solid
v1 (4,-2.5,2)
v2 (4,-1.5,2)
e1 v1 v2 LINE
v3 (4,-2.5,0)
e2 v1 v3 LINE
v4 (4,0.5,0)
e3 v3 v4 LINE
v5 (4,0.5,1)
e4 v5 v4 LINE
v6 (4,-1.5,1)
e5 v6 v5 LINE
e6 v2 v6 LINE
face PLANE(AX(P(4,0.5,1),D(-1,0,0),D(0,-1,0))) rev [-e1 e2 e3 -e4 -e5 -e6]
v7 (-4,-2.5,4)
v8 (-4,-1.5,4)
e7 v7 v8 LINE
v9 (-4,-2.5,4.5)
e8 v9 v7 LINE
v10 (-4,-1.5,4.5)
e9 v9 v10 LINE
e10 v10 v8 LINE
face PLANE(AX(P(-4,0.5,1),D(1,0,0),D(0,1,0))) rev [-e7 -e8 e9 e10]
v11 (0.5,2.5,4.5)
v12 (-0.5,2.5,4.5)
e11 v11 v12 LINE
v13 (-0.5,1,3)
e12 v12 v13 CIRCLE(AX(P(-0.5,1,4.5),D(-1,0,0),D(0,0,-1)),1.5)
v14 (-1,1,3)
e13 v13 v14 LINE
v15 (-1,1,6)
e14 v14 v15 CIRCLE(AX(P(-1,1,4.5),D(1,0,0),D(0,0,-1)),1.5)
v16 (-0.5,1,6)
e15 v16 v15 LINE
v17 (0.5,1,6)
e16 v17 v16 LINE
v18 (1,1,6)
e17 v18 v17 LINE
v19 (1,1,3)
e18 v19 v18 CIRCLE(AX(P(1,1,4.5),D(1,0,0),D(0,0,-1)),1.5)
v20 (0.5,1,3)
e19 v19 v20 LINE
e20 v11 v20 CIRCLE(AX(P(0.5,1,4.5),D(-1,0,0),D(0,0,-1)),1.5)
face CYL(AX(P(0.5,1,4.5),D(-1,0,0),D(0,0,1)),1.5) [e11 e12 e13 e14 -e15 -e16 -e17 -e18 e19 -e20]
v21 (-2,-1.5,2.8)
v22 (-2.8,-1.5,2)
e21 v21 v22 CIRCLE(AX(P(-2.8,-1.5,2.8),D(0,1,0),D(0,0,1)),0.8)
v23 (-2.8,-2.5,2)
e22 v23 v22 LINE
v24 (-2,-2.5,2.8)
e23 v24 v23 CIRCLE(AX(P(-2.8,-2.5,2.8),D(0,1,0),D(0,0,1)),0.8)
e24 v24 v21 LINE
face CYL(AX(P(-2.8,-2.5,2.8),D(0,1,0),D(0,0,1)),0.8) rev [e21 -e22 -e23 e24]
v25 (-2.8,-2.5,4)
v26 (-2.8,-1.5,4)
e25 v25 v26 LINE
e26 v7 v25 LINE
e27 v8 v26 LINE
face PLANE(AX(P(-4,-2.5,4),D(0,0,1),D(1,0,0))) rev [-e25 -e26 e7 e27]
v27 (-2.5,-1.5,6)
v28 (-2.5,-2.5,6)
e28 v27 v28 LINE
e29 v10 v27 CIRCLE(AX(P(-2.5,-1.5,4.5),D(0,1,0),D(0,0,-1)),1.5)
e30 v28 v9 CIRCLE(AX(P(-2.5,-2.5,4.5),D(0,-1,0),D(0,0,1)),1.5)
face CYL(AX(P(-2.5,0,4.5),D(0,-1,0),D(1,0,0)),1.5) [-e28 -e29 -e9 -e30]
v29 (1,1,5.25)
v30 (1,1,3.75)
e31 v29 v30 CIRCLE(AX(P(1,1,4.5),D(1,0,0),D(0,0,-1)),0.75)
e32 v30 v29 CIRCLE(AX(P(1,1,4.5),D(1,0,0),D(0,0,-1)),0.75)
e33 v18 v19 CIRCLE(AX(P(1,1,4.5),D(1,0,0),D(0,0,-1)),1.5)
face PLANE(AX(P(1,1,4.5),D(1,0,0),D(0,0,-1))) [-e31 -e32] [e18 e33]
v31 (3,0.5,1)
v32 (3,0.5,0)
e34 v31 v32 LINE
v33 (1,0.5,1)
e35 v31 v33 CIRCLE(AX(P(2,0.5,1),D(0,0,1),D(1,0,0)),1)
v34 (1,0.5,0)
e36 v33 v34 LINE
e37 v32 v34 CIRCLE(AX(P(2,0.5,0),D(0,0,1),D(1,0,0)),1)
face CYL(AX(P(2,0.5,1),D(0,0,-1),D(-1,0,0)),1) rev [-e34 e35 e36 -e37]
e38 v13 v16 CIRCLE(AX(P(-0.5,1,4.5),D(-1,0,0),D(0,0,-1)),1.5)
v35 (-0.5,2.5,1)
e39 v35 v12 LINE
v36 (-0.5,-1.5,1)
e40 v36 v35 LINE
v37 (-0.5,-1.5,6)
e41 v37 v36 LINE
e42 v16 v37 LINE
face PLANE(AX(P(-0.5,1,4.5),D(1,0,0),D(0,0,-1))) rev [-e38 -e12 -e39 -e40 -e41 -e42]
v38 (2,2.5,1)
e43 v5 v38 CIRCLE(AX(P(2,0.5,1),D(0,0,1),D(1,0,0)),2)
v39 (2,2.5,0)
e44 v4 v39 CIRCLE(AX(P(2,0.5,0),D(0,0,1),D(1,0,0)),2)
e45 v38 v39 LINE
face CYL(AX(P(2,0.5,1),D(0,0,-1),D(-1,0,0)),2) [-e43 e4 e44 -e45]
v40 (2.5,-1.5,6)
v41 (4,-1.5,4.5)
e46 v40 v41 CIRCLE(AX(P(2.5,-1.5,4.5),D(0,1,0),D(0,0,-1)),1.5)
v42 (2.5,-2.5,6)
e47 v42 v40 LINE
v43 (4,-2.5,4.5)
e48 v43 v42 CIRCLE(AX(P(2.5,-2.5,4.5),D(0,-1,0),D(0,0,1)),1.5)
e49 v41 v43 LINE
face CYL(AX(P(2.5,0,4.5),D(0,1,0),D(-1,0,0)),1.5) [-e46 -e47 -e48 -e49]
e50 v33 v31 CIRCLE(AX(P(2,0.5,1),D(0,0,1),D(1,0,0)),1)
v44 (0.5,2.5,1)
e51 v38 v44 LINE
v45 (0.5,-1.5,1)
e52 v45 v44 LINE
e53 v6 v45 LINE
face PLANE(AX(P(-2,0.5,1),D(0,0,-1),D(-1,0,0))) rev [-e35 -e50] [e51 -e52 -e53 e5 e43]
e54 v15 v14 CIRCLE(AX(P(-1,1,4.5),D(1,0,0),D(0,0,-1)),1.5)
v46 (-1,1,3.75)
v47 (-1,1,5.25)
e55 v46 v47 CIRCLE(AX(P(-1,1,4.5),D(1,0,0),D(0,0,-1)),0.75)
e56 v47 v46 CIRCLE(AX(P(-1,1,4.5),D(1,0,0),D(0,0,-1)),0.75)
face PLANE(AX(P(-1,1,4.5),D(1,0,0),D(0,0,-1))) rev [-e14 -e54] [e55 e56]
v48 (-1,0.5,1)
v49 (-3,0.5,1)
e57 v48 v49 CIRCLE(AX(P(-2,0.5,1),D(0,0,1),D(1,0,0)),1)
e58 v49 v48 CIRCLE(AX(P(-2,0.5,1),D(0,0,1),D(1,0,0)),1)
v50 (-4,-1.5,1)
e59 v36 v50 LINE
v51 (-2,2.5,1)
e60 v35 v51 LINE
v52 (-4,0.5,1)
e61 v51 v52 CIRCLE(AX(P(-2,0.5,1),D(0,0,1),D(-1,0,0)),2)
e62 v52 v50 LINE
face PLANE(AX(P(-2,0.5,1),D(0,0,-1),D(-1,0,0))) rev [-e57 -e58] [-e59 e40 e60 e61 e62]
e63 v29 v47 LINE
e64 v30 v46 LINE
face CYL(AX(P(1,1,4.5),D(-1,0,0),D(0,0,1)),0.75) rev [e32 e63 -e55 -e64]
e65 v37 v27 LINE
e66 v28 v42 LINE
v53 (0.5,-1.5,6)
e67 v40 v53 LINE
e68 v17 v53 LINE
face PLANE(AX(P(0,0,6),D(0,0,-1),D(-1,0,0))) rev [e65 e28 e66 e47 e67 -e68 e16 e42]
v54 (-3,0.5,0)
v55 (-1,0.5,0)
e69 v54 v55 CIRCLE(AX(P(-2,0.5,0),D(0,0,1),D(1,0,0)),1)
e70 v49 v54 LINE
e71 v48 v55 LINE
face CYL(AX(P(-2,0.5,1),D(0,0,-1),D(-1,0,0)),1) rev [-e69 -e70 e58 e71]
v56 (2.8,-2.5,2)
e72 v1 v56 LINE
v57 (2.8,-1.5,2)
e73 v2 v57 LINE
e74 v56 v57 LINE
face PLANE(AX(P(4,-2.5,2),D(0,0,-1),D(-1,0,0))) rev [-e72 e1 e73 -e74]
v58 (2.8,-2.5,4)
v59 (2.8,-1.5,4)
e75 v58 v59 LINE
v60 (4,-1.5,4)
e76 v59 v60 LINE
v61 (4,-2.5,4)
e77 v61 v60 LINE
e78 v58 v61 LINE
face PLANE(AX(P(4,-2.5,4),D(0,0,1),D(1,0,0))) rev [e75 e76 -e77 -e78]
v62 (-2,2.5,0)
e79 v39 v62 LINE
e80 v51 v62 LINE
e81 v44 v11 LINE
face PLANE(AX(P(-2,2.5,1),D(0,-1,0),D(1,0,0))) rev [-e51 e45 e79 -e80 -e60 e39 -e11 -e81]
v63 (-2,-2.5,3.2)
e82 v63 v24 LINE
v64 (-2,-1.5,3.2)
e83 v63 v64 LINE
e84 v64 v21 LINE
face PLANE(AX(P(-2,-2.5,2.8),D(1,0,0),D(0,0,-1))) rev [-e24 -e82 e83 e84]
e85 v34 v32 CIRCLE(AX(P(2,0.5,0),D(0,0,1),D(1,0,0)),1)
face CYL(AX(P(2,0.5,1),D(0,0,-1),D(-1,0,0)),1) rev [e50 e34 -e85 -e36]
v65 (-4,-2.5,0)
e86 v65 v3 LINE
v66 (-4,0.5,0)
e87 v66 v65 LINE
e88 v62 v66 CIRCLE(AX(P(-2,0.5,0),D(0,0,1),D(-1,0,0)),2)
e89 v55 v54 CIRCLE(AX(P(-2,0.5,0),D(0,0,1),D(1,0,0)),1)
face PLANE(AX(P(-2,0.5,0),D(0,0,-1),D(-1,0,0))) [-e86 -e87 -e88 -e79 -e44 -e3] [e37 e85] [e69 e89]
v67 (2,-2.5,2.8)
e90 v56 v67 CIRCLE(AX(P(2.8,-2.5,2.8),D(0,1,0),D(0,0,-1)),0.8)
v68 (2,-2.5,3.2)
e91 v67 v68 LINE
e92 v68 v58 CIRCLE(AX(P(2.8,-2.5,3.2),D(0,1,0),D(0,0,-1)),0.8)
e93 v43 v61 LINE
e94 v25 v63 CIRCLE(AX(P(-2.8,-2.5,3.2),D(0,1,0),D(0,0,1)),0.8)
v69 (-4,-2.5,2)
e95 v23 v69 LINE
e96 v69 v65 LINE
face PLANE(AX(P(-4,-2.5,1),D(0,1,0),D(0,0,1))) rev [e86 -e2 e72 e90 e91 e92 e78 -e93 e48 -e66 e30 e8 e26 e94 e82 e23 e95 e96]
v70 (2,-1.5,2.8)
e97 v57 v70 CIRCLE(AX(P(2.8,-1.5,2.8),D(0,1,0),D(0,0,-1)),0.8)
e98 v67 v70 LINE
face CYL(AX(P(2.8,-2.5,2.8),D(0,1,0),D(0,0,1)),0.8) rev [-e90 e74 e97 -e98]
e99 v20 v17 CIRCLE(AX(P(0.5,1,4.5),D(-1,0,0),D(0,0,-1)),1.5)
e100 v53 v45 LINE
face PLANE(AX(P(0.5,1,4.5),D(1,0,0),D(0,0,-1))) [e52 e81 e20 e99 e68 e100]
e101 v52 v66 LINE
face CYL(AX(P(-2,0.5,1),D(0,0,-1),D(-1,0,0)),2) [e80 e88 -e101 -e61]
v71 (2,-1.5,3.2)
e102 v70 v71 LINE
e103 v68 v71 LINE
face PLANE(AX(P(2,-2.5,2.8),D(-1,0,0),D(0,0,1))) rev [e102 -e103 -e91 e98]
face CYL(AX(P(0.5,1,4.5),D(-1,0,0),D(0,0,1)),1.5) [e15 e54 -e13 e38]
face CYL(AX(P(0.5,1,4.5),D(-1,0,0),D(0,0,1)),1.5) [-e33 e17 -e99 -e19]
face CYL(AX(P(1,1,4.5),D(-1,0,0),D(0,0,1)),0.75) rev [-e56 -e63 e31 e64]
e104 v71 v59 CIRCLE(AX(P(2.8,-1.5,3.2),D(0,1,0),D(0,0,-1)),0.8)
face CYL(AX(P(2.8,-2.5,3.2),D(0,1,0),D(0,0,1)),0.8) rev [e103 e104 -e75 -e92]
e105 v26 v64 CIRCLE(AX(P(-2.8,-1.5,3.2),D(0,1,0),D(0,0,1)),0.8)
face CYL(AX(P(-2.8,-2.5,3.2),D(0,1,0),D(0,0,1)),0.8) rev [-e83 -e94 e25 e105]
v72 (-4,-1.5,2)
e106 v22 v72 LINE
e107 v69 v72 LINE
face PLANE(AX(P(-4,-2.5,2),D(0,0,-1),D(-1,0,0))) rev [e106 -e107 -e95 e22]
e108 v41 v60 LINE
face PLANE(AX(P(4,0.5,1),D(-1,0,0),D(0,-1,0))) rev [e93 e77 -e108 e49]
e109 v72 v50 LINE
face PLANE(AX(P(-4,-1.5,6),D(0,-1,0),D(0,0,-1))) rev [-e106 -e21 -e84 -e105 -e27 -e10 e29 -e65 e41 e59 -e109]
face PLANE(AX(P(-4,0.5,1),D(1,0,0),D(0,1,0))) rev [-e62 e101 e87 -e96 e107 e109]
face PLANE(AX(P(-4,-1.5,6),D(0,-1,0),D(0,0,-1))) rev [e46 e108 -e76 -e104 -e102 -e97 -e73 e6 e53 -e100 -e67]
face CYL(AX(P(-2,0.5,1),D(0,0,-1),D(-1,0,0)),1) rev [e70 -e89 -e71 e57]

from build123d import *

# Parameters (mm, degrees)
BASE_PLATE_SKETCH_R        = 1
BASE_PLATE_DEPTH           = 1
UPRIGHT_WALL_SKETCH_W      = 8
UPRIGHT_WALL_SKETCH_H      = 1
UPRIGHT_WALL_DEPTH         = 5
SLOT_CUTS_DEPTH            = 9.246211251
SIDE_LUG_DEPTH             = 0.5
PIN_BOSS_SKETCH_R          = 1.5
PIN_BOSS_SKETCH_R_2        = 0.75
PIN_BOSS_3_DEPTH           = 1
PIN_BORE_SKETCH_R          = 0.75
PIN_BORE_DEPTH             = 8.90569415
UPRIGHT_WALL_FILLET_R1_5_R = 1.5


with BuildPart() as part:
    # Base Plate Sketch → Base Plate (new body)
    with BuildSketch(Plane.XY):
        with BuildLine():
            Line((-2, 2.5), (2, 2.5))
            ThreePointArc((2, 2.5), (3.414213562, 1.914213562), (4, 0.5))
            Line((4, 0.5), (4, -2.5))
            Line((4, -2.5), (-4, -2.5))
            Line((-4, -2.5), (-4, 0.5))
            ThreePointArc((-4, 0.5), (-3.414213562, 1.914213562), (-2, 2.5))
        make_face()
        with Locations((-2, 0.5)):
            Circle(BASE_PLATE_SKETCH_R, mode=Mode.SUBTRACT)
        with Locations((2, 0.5)):
            Circle(BASE_PLATE_SKETCH_R, mode=Mode.SUBTRACT)
    extrude(amount=BASE_PLATE_DEPTH)

    # Upright Wall Sketch → Upright Wall (add)
    with BuildSketch(Plane.XY.offset(1)):
        with Locations((0, -2)):
            Rectangle(UPRIGHT_WALL_SKETCH_W, UPRIGHT_WALL_SKETCH_H)
    extrude(amount=UPRIGHT_WALL_DEPTH)

    # Slot Cuts Sketch → Slot Cuts (cut, through all)
    with BuildSketch(Plane(origin=(0, -1.5, 0), x_dir=(1, 0, 0), z_dir=(0, 1, 0))):
        with BuildLine():
            Line((-4, -2), (-2.8, -2))
            ThreePointArc((-2.8, -2), (-2.234314575, -2.234314575), (-2, -2.8))
            Line((-2, -2.8), (-2, -3.2))
            ThreePointArc((-2, -3.2), (-2.234314575, -3.765685425), (-2.8, -4))
            Line((-2.8, -4), (-4, -4))
            Line((-4, -4), (-4, -2))
        make_face()
        with BuildLine():
            Line((4, -2), (2.8, -2))
            ThreePointArc((2.8, -2), (2.234314575, -2.234314575), (2, -2.8))
            Line((2, -2.8), (2, -3.2))
            ThreePointArc((2, -3.2), (2.234314575, -3.765685425), (2.8, -4))
            Line((2.8, -4), (4, -4))
            Line((4, -4), (4, -2))
        make_face()
    extrude(amount=-SLOT_CUTS_DEPTH, mode=Mode.SUBTRACT)

    # Side Lug Sketch → Side Lug (add, symmetric)
    with BuildSketch(Plane(origin=(0, 0, 0), x_dir=(0, 0, -1), z_dir=(1, 0, 0))):
        with BuildLine():
            Line((-1, 2.5), (-4.5, 2.5))
            ThreePointArc((-4.5, 2.5), (-5.560660172, 2.060660172), (-6, 1))
            Line((-6, 1), (-6, -1.5))
            Line((-6, -1.5), (-1, -1.5))
            Line((-1, -1.5), (-1, 2.5))
        make_face()
    extrude(amount=SIDE_LUG_DEPTH, both=True)

    # Pin Boss Sketch → Pin Boss Ø3 (add, symmetric)
    with BuildSketch(Plane(origin=(0, 0, 0), x_dir=(0, 0, -1), z_dir=(1, 0, 0))):
        with Locations((-4.5, 1)):
            Circle(PIN_BOSS_SKETCH_R)
        with Locations((-4.5, 1)):
            Circle(PIN_BOSS_SKETCH_R_2, mode=Mode.SUBTRACT)
    extrude(amount=PIN_BOSS_3_DEPTH, both=True)

    # Pin Bore Sketch → Pin Bore (cut, through all)
    with BuildSketch(Plane(origin=(0.5, 0, 0), x_dir=(0, 0, -1), z_dir=(1, 0, 0))):
        with Locations((-4.5, 1)):
            Circle(PIN_BORE_SKETCH_R)
    extrude(amount=-PIN_BORE_DEPTH, mode=Mode.SUBTRACT)

    # Upright Wall Fillet R1.5
    upright_wall_fillet_r1_5_edges = [part.edges().sort_by_distance(p)[0] for p in [
        (-4, -2, 6),
        (4, -2, 6),
    ]]
    fillet(upright_wall_fillet_r1_5_edges, radius=UPRIGHT_WALL_FILLET_R1_5_R)


solid = part.part
